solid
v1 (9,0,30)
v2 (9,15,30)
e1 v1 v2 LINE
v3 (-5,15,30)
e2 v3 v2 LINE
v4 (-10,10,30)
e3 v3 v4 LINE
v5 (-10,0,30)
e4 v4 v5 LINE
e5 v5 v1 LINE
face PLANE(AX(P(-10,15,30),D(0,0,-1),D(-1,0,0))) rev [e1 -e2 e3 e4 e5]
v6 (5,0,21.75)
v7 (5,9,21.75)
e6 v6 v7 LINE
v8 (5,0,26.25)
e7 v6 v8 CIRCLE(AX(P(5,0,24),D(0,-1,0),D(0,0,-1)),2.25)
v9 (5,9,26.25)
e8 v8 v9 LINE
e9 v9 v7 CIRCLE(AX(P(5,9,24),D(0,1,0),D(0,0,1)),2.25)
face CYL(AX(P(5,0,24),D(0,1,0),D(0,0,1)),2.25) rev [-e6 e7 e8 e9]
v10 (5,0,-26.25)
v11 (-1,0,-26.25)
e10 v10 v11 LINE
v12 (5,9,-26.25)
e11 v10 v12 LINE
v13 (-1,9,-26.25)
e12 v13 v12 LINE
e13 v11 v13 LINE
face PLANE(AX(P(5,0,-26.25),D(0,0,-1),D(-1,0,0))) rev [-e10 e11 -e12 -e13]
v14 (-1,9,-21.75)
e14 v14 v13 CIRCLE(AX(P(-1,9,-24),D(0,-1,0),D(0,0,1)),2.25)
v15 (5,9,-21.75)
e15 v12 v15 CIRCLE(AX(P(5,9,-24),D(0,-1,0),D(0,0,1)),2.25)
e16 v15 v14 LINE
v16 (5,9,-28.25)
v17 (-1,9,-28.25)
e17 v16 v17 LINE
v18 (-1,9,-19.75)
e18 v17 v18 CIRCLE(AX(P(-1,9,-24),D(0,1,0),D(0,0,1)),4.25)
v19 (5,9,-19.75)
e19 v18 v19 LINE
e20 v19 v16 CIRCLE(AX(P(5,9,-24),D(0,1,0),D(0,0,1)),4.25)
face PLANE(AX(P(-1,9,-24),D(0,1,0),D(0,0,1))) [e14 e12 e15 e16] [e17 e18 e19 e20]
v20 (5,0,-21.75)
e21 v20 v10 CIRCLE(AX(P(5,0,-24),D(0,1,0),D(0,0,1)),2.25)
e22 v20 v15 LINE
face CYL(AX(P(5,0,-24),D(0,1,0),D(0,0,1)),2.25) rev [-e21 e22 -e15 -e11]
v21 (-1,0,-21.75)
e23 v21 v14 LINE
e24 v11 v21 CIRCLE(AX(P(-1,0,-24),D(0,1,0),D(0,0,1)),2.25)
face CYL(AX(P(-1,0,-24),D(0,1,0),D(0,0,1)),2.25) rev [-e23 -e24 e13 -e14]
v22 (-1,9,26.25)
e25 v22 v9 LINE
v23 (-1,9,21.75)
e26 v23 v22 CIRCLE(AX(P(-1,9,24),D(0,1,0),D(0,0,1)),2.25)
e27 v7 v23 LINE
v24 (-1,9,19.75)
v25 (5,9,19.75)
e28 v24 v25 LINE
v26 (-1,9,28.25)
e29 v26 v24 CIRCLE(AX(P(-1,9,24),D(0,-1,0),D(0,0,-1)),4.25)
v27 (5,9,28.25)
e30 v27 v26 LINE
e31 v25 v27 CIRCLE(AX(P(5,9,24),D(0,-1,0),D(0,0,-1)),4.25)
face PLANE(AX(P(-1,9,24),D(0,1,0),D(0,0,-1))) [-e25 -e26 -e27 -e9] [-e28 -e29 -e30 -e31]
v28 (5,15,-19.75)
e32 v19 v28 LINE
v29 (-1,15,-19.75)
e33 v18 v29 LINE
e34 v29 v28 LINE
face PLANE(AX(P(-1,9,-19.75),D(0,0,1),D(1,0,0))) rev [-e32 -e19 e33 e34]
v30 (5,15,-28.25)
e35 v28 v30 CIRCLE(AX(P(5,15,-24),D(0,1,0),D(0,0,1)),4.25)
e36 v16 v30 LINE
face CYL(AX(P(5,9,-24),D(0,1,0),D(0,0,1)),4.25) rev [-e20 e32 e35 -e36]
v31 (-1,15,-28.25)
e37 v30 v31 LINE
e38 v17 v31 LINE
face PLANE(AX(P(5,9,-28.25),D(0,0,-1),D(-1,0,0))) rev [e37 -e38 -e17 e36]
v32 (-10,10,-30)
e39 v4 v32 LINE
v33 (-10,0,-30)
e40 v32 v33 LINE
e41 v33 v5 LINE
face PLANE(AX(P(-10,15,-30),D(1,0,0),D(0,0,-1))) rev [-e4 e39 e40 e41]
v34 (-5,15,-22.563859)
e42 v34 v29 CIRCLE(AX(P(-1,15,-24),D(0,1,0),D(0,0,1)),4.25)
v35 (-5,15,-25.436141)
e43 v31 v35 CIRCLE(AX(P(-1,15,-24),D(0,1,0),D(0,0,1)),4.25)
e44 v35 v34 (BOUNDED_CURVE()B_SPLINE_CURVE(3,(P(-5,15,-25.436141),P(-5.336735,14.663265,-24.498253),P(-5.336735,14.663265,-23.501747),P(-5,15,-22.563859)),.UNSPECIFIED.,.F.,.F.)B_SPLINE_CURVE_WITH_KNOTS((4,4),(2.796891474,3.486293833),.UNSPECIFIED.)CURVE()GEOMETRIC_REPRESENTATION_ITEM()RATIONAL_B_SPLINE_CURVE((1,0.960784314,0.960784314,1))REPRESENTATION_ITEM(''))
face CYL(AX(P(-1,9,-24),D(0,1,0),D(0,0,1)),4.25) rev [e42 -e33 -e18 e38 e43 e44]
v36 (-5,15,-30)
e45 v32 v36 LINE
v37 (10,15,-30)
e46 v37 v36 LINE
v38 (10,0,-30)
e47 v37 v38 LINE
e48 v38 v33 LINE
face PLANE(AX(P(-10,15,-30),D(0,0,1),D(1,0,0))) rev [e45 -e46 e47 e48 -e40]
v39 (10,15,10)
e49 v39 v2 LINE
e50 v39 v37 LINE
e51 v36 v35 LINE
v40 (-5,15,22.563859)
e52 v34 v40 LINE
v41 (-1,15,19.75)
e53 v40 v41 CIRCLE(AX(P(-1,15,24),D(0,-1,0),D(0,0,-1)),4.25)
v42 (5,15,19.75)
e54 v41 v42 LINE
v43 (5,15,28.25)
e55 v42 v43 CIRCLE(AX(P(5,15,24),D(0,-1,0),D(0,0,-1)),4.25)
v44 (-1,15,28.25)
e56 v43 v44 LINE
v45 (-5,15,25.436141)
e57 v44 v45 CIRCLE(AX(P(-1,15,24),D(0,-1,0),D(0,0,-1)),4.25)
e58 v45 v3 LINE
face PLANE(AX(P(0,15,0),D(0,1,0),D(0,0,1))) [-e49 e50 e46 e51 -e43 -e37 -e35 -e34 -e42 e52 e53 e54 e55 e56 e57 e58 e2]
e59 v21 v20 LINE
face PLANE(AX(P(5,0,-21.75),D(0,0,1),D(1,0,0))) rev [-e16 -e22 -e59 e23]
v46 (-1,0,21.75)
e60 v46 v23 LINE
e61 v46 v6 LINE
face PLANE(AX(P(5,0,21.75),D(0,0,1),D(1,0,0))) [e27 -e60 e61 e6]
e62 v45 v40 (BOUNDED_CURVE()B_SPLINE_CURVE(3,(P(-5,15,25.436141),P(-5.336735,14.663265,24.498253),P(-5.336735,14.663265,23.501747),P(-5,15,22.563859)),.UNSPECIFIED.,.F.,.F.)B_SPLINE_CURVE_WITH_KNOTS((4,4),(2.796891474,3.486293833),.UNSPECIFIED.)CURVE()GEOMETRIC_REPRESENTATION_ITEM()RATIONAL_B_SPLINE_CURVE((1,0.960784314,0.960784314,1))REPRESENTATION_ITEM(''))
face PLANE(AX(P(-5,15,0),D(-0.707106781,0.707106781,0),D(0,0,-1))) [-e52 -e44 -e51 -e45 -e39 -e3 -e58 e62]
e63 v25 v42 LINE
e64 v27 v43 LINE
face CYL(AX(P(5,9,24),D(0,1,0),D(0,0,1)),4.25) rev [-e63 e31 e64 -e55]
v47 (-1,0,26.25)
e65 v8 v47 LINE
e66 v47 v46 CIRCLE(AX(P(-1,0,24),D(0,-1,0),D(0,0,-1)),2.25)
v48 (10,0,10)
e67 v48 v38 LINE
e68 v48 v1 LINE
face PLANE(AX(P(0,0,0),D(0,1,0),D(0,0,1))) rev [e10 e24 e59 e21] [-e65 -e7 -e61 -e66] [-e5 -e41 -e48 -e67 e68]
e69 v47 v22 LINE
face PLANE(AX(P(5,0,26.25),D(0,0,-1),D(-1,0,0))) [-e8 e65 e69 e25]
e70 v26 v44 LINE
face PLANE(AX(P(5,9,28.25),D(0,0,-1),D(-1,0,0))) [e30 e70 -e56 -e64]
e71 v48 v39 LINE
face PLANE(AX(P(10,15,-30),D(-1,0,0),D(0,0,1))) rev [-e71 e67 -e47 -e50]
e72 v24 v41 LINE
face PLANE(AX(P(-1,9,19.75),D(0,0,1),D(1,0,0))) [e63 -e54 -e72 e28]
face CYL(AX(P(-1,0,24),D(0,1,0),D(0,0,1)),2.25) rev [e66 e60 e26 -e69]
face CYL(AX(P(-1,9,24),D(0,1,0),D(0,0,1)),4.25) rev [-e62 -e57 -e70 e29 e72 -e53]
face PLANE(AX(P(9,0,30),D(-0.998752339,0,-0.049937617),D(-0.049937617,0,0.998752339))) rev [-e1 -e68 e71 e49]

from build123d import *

# Parameters (mm, degrees)
SKETCH1_W           = 20
SKETCH1_H           = 60
BOSS_EXTRUDE1_DEPTH = 15
CHAMFER1_SIZE       = 5
CUT_EXTRUDE1_DEPTH  = 36
CUT_EXTRUDE2_DEPTH  = 36
CUT_EXTRUDE3_DEPTH  = 6


with BuildPart() as part:
    # Sketch1 → Boss-Extrude1 (new body)
    with BuildSketch(Plane(origin=(0, 0, 0), x_dir=(1, 0, 0), z_dir=(0, 1, 0))):
        Rectangle(SKETCH1_W, SKETCH1_H)
    extrude(amount=BOSS_EXTRUDE1_DEPTH)

    # Chamfer1
    chamfer1_edges = [part.edges().sort_by_distance(p)[0] for p in [
        (-10, 15, 0),
    ]]
    chamfer(chamfer1_edges, length=CHAMFER1_SIZE)

    # Sketch2 → Cut-Extrude1 (cut, through all)
    with BuildSketch(Plane(origin=(0, 15, 0), x_dir=(1, 0, 0), z_dir=(0, 1, 0))):
        Polygon((10, -30), (9, -30), (10, -10), align=None)
    extrude(amount=-CUT_EXTRUDE1_DEPTH, mode=Mode.SUBTRACT)

    # Sketch3 → Cut-Extrude2 (cut, through all)
    with BuildSketch(Plane(origin=(0, 15, 0), x_dir=(1, 0, 0), z_dir=(0, 1, 0))):
        with BuildLine():
            Line((5, 21.75), (-1, 21.75))
            ThreePointArc((-1, 21.75), (-3.25, 24), (-1, 26.25))
            Line((-1, 26.25), (5, 26.25))
            ThreePointArc((5, 26.25), (7.25, 24), (5, 21.75))
        make_face()
    cut_extrude2 = extrude(amount=-CUT_EXTRUDE2_DEPTH, mode=Mode.SUBTRACT)

    # Sketch4 → Cut-Extrude3 (cut)
    with BuildSketch(Plane(origin=(0, 15, 0), x_dir=(1, 0, 0), z_dir=(0, 1, 0))):
        with BuildLine():
            Line((-1, 19.75), (5, 19.75))
            ThreePointArc((5, 19.75), (9.25, 24), (5, 28.25))
            Line((5, 28.25), (-1, 28.25))
            ThreePointArc((-1, 28.25), (-5.25, 24), (-1, 19.75))
        make_face()
    cut_extrude3 = extrude(amount=-CUT_EXTRUDE3_DEPTH, mode=Mode.SUBTRACT)

    # Mirror1: Cut-Extrude2, Cut-Extrude3 across plane
    add(cut_extrude2.mirror(Plane.XY), mode=Mode.SUBTRACT)
    add(cut_extrude3.mirror(Plane.XY), mode=Mode.SUBTRACT)


solid = part.part
